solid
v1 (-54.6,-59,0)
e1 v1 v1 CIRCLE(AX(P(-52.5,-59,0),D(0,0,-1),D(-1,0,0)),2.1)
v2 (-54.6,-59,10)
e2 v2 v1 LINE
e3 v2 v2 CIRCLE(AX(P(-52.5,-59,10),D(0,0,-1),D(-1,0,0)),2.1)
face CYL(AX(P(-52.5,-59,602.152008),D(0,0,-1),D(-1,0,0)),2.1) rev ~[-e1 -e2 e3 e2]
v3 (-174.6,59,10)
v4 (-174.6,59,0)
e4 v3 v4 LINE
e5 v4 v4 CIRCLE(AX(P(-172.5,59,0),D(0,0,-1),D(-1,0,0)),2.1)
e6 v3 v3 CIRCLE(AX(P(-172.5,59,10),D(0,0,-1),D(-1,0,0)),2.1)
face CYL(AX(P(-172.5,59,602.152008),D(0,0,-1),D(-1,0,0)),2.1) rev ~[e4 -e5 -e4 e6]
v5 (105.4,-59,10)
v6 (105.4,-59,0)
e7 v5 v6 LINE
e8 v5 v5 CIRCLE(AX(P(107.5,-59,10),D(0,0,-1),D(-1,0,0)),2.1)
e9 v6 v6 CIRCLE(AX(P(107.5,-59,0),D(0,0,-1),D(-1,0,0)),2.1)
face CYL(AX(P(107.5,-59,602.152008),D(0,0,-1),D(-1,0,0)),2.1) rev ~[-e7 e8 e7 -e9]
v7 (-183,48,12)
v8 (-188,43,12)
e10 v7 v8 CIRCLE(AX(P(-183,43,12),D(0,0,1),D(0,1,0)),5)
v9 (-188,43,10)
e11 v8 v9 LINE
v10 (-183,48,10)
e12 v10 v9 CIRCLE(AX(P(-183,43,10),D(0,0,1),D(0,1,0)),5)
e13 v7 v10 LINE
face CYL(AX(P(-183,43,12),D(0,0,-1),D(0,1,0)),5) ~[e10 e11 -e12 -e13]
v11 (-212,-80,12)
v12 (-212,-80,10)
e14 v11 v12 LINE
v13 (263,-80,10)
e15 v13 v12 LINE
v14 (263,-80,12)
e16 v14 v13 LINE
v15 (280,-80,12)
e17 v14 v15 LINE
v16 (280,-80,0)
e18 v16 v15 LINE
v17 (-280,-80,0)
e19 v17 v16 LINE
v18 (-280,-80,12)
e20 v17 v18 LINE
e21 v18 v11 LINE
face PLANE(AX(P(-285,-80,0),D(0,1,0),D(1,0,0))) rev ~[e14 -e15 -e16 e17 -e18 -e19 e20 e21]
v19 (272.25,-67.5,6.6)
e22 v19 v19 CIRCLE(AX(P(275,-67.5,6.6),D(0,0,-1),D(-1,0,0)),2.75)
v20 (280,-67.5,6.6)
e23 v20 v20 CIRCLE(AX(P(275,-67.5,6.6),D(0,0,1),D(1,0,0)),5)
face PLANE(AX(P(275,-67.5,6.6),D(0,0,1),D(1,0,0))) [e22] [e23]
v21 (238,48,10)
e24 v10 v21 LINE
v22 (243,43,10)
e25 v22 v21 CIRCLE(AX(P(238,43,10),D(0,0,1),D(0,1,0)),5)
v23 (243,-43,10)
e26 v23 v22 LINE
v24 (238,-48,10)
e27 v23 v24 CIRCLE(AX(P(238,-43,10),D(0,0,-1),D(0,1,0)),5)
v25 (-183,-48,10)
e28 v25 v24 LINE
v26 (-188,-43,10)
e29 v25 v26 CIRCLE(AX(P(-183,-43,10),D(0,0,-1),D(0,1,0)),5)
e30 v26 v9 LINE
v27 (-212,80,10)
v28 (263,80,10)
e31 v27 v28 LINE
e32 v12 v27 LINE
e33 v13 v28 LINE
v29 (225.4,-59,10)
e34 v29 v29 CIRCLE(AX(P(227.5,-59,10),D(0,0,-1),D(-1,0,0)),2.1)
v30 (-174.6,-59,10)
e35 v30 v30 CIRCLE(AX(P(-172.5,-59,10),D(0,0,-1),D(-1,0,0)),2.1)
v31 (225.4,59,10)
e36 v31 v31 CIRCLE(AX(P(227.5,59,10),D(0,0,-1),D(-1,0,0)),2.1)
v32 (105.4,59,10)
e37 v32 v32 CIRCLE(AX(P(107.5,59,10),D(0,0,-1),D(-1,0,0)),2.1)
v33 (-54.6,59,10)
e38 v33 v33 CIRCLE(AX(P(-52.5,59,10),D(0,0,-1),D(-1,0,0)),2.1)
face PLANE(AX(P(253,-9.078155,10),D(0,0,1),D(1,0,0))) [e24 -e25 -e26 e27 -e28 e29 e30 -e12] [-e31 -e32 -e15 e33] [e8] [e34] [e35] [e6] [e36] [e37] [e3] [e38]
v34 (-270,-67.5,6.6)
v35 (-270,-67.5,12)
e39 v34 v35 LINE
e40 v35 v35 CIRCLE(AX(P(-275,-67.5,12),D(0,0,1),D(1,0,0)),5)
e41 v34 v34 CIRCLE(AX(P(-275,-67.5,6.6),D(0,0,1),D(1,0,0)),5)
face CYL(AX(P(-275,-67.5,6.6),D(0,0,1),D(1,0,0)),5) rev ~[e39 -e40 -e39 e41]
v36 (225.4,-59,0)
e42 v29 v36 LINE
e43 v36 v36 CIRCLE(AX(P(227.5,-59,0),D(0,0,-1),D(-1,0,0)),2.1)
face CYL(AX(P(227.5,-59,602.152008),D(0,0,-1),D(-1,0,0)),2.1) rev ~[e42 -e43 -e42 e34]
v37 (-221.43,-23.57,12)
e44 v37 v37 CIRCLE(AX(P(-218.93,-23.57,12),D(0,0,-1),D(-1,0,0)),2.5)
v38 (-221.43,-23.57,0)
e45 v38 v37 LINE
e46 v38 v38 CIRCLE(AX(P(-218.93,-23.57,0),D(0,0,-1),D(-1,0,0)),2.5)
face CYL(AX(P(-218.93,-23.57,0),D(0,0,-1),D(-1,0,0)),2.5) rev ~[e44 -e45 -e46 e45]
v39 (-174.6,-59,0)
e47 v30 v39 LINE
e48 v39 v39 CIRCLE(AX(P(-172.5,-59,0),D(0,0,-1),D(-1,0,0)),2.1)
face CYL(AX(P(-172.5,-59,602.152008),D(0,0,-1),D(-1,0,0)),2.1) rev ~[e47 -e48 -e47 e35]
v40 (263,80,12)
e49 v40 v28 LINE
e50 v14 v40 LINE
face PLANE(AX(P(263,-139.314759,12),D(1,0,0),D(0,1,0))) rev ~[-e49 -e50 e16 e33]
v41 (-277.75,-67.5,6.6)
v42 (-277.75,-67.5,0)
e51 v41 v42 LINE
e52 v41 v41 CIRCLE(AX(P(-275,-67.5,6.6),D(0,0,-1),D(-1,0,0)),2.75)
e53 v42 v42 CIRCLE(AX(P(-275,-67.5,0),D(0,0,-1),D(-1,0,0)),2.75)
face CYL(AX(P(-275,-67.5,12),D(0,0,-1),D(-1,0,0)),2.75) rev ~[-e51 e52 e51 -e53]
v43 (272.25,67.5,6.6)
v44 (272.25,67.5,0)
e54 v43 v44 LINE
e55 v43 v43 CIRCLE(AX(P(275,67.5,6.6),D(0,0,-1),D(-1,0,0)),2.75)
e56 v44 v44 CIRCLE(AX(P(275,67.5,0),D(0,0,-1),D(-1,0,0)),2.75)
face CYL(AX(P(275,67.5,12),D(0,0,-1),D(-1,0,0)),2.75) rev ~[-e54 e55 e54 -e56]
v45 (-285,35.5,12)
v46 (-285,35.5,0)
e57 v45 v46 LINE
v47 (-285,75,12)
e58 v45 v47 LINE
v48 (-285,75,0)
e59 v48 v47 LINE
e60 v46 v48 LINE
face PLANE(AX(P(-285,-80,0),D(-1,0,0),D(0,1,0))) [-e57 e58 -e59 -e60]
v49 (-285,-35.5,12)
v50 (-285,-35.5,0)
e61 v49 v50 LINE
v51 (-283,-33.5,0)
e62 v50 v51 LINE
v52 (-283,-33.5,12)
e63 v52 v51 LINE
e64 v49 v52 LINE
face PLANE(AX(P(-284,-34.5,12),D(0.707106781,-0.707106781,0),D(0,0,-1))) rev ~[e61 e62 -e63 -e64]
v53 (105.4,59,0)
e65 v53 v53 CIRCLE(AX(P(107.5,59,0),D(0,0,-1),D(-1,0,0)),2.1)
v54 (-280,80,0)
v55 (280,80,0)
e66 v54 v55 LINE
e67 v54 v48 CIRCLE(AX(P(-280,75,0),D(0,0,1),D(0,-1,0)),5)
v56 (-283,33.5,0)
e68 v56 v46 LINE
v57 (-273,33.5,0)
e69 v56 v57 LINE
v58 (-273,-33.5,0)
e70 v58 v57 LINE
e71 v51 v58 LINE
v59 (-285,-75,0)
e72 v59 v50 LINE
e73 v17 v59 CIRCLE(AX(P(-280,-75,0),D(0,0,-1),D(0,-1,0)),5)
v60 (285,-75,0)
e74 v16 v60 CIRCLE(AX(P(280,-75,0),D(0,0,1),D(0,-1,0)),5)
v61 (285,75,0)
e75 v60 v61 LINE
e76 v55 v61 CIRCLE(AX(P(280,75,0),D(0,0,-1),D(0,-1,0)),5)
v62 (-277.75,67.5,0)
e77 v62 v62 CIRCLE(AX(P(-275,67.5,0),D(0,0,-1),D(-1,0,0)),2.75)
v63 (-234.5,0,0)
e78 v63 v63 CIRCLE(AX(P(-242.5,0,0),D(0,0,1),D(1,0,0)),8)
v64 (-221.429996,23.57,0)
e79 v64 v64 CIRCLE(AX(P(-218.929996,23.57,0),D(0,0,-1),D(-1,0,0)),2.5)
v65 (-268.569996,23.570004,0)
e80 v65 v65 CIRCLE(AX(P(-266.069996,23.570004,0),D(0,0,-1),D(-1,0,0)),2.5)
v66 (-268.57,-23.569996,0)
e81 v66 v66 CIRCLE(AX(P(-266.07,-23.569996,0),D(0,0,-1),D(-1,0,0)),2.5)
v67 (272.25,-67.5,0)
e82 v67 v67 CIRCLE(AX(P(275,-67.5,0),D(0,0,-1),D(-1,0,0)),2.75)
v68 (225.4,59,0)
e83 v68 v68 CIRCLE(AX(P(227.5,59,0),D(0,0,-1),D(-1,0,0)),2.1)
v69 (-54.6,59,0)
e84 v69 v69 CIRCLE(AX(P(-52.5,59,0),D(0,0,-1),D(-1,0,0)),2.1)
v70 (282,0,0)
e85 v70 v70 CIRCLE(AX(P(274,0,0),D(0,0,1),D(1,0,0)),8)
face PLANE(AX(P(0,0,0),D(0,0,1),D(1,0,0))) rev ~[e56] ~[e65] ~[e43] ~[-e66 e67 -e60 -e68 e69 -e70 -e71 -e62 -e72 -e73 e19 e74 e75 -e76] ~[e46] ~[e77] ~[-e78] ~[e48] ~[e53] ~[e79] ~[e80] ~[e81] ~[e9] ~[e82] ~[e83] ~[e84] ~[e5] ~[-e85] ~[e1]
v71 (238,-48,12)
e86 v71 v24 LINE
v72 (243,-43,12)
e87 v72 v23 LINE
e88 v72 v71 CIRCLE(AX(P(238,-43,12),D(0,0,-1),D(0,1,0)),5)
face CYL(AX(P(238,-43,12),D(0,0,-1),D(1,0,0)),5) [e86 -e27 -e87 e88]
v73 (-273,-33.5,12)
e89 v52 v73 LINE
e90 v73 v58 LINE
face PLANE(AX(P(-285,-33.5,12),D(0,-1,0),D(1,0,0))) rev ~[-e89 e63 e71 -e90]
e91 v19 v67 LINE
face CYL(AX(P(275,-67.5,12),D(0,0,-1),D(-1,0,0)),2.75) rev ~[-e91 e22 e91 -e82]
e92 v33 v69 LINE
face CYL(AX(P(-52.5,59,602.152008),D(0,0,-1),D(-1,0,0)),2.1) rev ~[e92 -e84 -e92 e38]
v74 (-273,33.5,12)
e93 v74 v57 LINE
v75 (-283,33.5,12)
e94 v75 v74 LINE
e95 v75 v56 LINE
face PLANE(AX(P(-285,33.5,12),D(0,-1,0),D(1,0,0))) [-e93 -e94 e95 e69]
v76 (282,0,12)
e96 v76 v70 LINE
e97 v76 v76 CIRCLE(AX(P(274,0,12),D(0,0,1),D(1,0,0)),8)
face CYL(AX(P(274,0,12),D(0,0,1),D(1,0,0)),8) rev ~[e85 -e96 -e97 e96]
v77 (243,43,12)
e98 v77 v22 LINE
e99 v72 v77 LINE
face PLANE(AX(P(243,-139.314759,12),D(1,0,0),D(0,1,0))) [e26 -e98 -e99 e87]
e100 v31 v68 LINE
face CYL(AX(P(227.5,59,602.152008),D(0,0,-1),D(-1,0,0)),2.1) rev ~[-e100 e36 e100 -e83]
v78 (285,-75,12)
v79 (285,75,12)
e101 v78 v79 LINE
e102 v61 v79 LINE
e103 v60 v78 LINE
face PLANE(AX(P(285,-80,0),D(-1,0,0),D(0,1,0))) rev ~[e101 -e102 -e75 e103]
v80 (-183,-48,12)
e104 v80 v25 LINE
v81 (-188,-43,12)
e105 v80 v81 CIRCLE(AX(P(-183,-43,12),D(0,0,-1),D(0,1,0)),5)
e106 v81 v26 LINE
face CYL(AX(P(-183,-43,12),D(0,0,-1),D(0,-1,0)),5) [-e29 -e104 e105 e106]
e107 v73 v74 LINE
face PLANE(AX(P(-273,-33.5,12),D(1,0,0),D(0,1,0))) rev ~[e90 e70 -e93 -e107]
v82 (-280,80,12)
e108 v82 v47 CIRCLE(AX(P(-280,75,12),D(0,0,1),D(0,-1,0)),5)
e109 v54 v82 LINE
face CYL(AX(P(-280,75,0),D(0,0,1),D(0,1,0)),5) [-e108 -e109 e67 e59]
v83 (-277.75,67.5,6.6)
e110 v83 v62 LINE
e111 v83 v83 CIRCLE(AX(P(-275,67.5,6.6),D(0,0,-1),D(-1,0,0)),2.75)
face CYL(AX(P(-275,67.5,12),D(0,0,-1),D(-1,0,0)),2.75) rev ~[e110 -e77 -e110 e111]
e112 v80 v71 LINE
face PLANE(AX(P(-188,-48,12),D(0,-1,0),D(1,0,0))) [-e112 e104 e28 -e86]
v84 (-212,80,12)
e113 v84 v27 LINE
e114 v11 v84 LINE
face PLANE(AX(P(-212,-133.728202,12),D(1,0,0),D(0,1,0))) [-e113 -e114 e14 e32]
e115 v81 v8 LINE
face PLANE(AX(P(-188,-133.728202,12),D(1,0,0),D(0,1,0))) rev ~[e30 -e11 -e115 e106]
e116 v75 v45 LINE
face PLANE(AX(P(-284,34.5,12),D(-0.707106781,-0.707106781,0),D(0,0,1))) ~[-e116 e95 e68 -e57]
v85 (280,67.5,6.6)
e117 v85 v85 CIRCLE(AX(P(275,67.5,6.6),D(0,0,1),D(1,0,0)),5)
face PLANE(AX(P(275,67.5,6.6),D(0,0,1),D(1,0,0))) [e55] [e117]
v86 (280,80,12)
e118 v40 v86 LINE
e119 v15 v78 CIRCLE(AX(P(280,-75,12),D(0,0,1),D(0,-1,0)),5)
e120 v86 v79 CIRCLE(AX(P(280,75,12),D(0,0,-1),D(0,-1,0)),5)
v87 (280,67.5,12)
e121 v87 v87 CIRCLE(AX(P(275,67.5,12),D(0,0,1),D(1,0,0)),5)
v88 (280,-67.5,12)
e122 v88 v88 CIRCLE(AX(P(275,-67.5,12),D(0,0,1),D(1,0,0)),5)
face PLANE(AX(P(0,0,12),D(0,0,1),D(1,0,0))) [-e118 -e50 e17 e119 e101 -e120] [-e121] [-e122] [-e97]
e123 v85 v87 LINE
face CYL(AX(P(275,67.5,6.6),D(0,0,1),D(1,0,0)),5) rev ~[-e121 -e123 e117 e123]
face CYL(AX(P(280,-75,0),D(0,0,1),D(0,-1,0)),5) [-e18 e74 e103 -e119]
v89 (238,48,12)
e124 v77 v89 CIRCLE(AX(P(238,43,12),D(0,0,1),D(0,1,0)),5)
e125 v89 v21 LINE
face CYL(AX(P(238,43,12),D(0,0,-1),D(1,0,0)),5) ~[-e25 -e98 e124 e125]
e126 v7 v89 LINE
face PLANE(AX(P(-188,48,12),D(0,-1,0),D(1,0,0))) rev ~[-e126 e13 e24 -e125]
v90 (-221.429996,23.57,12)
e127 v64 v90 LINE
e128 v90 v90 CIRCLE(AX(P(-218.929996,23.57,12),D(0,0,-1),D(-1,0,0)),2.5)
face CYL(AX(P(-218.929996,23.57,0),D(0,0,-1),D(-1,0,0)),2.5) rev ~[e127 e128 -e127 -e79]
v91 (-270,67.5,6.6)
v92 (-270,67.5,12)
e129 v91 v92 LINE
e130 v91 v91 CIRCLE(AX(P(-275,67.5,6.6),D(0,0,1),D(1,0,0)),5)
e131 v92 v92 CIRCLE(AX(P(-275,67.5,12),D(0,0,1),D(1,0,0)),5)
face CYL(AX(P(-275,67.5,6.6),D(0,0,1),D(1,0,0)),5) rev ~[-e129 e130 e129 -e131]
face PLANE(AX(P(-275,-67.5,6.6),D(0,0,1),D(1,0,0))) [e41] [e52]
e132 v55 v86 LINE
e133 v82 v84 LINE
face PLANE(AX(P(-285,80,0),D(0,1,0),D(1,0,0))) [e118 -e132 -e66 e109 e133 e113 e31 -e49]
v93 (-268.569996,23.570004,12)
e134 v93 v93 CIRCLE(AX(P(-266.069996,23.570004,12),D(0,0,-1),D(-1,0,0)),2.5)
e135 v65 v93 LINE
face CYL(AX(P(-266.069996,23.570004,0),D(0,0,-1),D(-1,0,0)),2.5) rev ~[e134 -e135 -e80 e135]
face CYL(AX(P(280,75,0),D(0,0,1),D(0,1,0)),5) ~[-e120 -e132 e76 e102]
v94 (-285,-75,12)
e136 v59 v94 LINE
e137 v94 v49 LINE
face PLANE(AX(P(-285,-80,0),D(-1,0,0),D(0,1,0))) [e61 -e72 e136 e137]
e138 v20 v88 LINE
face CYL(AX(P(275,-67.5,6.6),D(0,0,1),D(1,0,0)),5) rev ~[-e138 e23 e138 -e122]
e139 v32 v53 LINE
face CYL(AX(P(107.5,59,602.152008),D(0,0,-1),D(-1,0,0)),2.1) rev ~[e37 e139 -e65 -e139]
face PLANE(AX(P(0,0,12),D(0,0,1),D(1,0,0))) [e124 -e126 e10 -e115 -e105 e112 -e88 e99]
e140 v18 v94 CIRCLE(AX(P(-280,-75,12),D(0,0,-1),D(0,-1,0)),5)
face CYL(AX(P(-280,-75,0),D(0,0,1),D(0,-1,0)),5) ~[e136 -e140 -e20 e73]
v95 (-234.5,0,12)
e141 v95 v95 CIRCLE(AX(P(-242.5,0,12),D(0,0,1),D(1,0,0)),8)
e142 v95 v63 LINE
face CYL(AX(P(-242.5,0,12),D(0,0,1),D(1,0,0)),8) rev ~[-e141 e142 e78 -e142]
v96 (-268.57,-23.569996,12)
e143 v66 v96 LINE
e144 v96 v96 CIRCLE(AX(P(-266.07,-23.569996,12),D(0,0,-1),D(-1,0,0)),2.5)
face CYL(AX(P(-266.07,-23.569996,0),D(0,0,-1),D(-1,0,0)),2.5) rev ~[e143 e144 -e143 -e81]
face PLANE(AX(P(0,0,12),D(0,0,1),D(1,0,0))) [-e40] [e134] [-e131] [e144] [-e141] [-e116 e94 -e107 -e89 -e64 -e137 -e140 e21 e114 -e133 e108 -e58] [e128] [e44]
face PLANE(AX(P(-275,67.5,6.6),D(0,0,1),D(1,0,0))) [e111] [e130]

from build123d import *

# Parameters (mm, degrees)
SKETCH1_W                                           = 570
SKETCH1_H                                           = 160
BOSS_EXTRUDE1_DEPTH                                 = 12
SKETCH2_W                                           = 24
SKETCH2_H                                           = 246.506816481
SKETCH2_W_2                                         = 20
SKETCH2_H_2                                         = 260.473208351
CUT_EXTRUDE1_DEPTH                                  = 2
SKETCH3_W                                           = 431
SKETCH3_H                                           = 32
CUT_EXTRUDE2_DEPTH                                  = 2
SKETCH4_W                                           = 12
SKETCH4_H                                           = 67
CUT_EXTRUDE3_DEPTH                                  = 297.258333216
M5_TAPPED_HOLE1_D                                   = 4.2
FILLET1_R                                           = 5
FILLET2_R                                           = 5
CHAMFER1_SIZE                                       = 2
CBORE_FOR_M5_HEX_SOCKET_HEAD_CAP_SCREW1_D           = 5.5
CBORE_FOR_M5_HEX_SOCKET_HEAD_CAP_SCREW1_CBORE_D     = 10
CBORE_FOR_M5_HEX_SOCKET_HEAD_CAP_SCREW1_CBORE_DEPTH = 5.4
SKETCH13_R                                          = 8
CUT_EXTRUDE4_DEPTH                                  = 18
SKETCH14_R                                          = 2.5
CUT_EXTRUDE5_DEPTH                                  = 12
SKETCH15_R                                          = 8
CUT_EXTRUDE6_DEPTH                                  = 12


with BuildPart() as part:
    # Sketch1 → Boss-Extrude1 (new body)
    with BuildSketch(Plane.XY):
        Rectangle(SKETCH1_W, SKETCH1_H)
    extrude(amount=BOSS_EXTRUDE1_DEPTH)

    # Sketch2 → Cut-Extrude1 (cut)
    with BuildSketch(Plane.XY.offset(12)):
        with Locations((-200, -10.474793902)):
            Rectangle(SKETCH2_W, SKETCH2_H)
        with Locations((253, -9.078154715)):
            Rectangle(SKETCH2_W_2, SKETCH2_H_2)
    extrude(amount=-CUT_EXTRUDE1_DEPTH, mode=Mode.SUBTRACT)

    # Sketch3 → Cut-Extrude2 (cut)
    with BuildSketch(Plane.XY.offset(12)):
        with Locations((27.5, 64)):
            Rectangle(SKETCH3_W, SKETCH3_H)
        with Locations((27.5, -64)):
            Rectangle(SKETCH3_W, SKETCH3_H)
    extrude(amount=-CUT_EXTRUDE2_DEPTH, mode=Mode.SUBTRACT)

    # Sketch4 → Cut-Extrude3 (cut, through all)
    with BuildSketch(Plane.XY.offset(12)):
        with Locations((-279, 0)):
            Rectangle(SKETCH4_W, SKETCH4_H)
    extrude(amount=-CUT_EXTRUDE3_DEPTH, mode=Mode.SUBTRACT)

    # M5 Tapped Hole1 (through all)
    with Locations(Plane.XY.offset(10)):
        with Locations((227.5, -59), (107.5, -59), (-172.5, -59), (-52.5, -59), (-172.5, 59), (-52.5, 59), (107.5, 59), (227.5, 59)):
            Hole(M5_TAPPED_HOLE1_D / 2)

    # Fillet1
    fillet1_edges = [part.edges().sort_by_distance(p)[0] for p in [
        (-188, 48, 11),
        (243, 48, 11),
        (-188, -48, 11),
        (243, -48, 11),
    ]]
    fillet(fillet1_edges, radius=FILLET1_R)

    # Fillet2
    fillet2_edges = [part.edges().sort_by_distance(p)[0] for p in [
        (285, -80, 6),
        (-285, -80, 6),
        (-285, 80, 6),
        (285, 80, 6),
    ]]
    fillet(fillet2_edges, radius=FILLET2_R)

    # Chamfer1
    chamfer1_edges = [part.edges().sort_by_distance(p)[0] for p in [
        (-285, -33.5, 6),
        (-285, 33.5, 6),
    ]]
    chamfer(chamfer1_edges, length=CHAMFER1_SIZE)

    # CBORE for M5 Hex Socket Head Cap Screw1 (through all)
    with Locations(Plane.XY.offset(12)):
        with Locations((275, 67.5), (-275, -67.5), (-275, 67.5), (275, -67.5)):
            CounterBoreHole(CBORE_FOR_M5_HEX_SOCKET_HEAD_CAP_SCREW1_D / 2, CBORE_FOR_M5_HEX_SOCKET_HEAD_CAP_SCREW1_CBORE_D / 2, CBORE_FOR_M5_HEX_SOCKET_HEAD_CAP_SCREW1_CBORE_DEPTH)

    # Sketch13 → Cut-Extrude4 (cut)
    with BuildSketch(Plane.XY.offset(12)):
        with Locations((-242.5, 0)):
            Circle(SKETCH13_R)
    extrude(amount=-CUT_EXTRUDE4_DEPTH, mode=Mode.SUBTRACT)

    # Sketch14 → Cut-Extrude5 (cut)
    with BuildSketch(Plane(origin=(0, 0, 0), x_dir=(-1, 0, 0), z_dir=(0, 0, -1))):
        with Locations((218.93, -23.570000001)):
            Circle(SKETCH14_R)
        with Locations((266.07, -23.569995906)):
            Circle(SKETCH14_R)
        with Locations((266.069995906, 23.570004094)):
            Circle(SKETCH14_R)
        with Locations((218.929995906, 23.569999999)):
            Circle(SKETCH14_R)
    extrude(amount=-CUT_EXTRUDE5_DEPTH, mode=Mode.SUBTRACT)

    # Sketch15 → Cut-Extrude6 (cut)
    with BuildSketch(Plane.XY.offset(12)):
        with Locations((274, 0)):
            Circle(SKETCH15_R)
    extrude(amount=-CUT_EXTRUDE6_DEPTH, mode=Mode.SUBTRACT)


solid = part.part
